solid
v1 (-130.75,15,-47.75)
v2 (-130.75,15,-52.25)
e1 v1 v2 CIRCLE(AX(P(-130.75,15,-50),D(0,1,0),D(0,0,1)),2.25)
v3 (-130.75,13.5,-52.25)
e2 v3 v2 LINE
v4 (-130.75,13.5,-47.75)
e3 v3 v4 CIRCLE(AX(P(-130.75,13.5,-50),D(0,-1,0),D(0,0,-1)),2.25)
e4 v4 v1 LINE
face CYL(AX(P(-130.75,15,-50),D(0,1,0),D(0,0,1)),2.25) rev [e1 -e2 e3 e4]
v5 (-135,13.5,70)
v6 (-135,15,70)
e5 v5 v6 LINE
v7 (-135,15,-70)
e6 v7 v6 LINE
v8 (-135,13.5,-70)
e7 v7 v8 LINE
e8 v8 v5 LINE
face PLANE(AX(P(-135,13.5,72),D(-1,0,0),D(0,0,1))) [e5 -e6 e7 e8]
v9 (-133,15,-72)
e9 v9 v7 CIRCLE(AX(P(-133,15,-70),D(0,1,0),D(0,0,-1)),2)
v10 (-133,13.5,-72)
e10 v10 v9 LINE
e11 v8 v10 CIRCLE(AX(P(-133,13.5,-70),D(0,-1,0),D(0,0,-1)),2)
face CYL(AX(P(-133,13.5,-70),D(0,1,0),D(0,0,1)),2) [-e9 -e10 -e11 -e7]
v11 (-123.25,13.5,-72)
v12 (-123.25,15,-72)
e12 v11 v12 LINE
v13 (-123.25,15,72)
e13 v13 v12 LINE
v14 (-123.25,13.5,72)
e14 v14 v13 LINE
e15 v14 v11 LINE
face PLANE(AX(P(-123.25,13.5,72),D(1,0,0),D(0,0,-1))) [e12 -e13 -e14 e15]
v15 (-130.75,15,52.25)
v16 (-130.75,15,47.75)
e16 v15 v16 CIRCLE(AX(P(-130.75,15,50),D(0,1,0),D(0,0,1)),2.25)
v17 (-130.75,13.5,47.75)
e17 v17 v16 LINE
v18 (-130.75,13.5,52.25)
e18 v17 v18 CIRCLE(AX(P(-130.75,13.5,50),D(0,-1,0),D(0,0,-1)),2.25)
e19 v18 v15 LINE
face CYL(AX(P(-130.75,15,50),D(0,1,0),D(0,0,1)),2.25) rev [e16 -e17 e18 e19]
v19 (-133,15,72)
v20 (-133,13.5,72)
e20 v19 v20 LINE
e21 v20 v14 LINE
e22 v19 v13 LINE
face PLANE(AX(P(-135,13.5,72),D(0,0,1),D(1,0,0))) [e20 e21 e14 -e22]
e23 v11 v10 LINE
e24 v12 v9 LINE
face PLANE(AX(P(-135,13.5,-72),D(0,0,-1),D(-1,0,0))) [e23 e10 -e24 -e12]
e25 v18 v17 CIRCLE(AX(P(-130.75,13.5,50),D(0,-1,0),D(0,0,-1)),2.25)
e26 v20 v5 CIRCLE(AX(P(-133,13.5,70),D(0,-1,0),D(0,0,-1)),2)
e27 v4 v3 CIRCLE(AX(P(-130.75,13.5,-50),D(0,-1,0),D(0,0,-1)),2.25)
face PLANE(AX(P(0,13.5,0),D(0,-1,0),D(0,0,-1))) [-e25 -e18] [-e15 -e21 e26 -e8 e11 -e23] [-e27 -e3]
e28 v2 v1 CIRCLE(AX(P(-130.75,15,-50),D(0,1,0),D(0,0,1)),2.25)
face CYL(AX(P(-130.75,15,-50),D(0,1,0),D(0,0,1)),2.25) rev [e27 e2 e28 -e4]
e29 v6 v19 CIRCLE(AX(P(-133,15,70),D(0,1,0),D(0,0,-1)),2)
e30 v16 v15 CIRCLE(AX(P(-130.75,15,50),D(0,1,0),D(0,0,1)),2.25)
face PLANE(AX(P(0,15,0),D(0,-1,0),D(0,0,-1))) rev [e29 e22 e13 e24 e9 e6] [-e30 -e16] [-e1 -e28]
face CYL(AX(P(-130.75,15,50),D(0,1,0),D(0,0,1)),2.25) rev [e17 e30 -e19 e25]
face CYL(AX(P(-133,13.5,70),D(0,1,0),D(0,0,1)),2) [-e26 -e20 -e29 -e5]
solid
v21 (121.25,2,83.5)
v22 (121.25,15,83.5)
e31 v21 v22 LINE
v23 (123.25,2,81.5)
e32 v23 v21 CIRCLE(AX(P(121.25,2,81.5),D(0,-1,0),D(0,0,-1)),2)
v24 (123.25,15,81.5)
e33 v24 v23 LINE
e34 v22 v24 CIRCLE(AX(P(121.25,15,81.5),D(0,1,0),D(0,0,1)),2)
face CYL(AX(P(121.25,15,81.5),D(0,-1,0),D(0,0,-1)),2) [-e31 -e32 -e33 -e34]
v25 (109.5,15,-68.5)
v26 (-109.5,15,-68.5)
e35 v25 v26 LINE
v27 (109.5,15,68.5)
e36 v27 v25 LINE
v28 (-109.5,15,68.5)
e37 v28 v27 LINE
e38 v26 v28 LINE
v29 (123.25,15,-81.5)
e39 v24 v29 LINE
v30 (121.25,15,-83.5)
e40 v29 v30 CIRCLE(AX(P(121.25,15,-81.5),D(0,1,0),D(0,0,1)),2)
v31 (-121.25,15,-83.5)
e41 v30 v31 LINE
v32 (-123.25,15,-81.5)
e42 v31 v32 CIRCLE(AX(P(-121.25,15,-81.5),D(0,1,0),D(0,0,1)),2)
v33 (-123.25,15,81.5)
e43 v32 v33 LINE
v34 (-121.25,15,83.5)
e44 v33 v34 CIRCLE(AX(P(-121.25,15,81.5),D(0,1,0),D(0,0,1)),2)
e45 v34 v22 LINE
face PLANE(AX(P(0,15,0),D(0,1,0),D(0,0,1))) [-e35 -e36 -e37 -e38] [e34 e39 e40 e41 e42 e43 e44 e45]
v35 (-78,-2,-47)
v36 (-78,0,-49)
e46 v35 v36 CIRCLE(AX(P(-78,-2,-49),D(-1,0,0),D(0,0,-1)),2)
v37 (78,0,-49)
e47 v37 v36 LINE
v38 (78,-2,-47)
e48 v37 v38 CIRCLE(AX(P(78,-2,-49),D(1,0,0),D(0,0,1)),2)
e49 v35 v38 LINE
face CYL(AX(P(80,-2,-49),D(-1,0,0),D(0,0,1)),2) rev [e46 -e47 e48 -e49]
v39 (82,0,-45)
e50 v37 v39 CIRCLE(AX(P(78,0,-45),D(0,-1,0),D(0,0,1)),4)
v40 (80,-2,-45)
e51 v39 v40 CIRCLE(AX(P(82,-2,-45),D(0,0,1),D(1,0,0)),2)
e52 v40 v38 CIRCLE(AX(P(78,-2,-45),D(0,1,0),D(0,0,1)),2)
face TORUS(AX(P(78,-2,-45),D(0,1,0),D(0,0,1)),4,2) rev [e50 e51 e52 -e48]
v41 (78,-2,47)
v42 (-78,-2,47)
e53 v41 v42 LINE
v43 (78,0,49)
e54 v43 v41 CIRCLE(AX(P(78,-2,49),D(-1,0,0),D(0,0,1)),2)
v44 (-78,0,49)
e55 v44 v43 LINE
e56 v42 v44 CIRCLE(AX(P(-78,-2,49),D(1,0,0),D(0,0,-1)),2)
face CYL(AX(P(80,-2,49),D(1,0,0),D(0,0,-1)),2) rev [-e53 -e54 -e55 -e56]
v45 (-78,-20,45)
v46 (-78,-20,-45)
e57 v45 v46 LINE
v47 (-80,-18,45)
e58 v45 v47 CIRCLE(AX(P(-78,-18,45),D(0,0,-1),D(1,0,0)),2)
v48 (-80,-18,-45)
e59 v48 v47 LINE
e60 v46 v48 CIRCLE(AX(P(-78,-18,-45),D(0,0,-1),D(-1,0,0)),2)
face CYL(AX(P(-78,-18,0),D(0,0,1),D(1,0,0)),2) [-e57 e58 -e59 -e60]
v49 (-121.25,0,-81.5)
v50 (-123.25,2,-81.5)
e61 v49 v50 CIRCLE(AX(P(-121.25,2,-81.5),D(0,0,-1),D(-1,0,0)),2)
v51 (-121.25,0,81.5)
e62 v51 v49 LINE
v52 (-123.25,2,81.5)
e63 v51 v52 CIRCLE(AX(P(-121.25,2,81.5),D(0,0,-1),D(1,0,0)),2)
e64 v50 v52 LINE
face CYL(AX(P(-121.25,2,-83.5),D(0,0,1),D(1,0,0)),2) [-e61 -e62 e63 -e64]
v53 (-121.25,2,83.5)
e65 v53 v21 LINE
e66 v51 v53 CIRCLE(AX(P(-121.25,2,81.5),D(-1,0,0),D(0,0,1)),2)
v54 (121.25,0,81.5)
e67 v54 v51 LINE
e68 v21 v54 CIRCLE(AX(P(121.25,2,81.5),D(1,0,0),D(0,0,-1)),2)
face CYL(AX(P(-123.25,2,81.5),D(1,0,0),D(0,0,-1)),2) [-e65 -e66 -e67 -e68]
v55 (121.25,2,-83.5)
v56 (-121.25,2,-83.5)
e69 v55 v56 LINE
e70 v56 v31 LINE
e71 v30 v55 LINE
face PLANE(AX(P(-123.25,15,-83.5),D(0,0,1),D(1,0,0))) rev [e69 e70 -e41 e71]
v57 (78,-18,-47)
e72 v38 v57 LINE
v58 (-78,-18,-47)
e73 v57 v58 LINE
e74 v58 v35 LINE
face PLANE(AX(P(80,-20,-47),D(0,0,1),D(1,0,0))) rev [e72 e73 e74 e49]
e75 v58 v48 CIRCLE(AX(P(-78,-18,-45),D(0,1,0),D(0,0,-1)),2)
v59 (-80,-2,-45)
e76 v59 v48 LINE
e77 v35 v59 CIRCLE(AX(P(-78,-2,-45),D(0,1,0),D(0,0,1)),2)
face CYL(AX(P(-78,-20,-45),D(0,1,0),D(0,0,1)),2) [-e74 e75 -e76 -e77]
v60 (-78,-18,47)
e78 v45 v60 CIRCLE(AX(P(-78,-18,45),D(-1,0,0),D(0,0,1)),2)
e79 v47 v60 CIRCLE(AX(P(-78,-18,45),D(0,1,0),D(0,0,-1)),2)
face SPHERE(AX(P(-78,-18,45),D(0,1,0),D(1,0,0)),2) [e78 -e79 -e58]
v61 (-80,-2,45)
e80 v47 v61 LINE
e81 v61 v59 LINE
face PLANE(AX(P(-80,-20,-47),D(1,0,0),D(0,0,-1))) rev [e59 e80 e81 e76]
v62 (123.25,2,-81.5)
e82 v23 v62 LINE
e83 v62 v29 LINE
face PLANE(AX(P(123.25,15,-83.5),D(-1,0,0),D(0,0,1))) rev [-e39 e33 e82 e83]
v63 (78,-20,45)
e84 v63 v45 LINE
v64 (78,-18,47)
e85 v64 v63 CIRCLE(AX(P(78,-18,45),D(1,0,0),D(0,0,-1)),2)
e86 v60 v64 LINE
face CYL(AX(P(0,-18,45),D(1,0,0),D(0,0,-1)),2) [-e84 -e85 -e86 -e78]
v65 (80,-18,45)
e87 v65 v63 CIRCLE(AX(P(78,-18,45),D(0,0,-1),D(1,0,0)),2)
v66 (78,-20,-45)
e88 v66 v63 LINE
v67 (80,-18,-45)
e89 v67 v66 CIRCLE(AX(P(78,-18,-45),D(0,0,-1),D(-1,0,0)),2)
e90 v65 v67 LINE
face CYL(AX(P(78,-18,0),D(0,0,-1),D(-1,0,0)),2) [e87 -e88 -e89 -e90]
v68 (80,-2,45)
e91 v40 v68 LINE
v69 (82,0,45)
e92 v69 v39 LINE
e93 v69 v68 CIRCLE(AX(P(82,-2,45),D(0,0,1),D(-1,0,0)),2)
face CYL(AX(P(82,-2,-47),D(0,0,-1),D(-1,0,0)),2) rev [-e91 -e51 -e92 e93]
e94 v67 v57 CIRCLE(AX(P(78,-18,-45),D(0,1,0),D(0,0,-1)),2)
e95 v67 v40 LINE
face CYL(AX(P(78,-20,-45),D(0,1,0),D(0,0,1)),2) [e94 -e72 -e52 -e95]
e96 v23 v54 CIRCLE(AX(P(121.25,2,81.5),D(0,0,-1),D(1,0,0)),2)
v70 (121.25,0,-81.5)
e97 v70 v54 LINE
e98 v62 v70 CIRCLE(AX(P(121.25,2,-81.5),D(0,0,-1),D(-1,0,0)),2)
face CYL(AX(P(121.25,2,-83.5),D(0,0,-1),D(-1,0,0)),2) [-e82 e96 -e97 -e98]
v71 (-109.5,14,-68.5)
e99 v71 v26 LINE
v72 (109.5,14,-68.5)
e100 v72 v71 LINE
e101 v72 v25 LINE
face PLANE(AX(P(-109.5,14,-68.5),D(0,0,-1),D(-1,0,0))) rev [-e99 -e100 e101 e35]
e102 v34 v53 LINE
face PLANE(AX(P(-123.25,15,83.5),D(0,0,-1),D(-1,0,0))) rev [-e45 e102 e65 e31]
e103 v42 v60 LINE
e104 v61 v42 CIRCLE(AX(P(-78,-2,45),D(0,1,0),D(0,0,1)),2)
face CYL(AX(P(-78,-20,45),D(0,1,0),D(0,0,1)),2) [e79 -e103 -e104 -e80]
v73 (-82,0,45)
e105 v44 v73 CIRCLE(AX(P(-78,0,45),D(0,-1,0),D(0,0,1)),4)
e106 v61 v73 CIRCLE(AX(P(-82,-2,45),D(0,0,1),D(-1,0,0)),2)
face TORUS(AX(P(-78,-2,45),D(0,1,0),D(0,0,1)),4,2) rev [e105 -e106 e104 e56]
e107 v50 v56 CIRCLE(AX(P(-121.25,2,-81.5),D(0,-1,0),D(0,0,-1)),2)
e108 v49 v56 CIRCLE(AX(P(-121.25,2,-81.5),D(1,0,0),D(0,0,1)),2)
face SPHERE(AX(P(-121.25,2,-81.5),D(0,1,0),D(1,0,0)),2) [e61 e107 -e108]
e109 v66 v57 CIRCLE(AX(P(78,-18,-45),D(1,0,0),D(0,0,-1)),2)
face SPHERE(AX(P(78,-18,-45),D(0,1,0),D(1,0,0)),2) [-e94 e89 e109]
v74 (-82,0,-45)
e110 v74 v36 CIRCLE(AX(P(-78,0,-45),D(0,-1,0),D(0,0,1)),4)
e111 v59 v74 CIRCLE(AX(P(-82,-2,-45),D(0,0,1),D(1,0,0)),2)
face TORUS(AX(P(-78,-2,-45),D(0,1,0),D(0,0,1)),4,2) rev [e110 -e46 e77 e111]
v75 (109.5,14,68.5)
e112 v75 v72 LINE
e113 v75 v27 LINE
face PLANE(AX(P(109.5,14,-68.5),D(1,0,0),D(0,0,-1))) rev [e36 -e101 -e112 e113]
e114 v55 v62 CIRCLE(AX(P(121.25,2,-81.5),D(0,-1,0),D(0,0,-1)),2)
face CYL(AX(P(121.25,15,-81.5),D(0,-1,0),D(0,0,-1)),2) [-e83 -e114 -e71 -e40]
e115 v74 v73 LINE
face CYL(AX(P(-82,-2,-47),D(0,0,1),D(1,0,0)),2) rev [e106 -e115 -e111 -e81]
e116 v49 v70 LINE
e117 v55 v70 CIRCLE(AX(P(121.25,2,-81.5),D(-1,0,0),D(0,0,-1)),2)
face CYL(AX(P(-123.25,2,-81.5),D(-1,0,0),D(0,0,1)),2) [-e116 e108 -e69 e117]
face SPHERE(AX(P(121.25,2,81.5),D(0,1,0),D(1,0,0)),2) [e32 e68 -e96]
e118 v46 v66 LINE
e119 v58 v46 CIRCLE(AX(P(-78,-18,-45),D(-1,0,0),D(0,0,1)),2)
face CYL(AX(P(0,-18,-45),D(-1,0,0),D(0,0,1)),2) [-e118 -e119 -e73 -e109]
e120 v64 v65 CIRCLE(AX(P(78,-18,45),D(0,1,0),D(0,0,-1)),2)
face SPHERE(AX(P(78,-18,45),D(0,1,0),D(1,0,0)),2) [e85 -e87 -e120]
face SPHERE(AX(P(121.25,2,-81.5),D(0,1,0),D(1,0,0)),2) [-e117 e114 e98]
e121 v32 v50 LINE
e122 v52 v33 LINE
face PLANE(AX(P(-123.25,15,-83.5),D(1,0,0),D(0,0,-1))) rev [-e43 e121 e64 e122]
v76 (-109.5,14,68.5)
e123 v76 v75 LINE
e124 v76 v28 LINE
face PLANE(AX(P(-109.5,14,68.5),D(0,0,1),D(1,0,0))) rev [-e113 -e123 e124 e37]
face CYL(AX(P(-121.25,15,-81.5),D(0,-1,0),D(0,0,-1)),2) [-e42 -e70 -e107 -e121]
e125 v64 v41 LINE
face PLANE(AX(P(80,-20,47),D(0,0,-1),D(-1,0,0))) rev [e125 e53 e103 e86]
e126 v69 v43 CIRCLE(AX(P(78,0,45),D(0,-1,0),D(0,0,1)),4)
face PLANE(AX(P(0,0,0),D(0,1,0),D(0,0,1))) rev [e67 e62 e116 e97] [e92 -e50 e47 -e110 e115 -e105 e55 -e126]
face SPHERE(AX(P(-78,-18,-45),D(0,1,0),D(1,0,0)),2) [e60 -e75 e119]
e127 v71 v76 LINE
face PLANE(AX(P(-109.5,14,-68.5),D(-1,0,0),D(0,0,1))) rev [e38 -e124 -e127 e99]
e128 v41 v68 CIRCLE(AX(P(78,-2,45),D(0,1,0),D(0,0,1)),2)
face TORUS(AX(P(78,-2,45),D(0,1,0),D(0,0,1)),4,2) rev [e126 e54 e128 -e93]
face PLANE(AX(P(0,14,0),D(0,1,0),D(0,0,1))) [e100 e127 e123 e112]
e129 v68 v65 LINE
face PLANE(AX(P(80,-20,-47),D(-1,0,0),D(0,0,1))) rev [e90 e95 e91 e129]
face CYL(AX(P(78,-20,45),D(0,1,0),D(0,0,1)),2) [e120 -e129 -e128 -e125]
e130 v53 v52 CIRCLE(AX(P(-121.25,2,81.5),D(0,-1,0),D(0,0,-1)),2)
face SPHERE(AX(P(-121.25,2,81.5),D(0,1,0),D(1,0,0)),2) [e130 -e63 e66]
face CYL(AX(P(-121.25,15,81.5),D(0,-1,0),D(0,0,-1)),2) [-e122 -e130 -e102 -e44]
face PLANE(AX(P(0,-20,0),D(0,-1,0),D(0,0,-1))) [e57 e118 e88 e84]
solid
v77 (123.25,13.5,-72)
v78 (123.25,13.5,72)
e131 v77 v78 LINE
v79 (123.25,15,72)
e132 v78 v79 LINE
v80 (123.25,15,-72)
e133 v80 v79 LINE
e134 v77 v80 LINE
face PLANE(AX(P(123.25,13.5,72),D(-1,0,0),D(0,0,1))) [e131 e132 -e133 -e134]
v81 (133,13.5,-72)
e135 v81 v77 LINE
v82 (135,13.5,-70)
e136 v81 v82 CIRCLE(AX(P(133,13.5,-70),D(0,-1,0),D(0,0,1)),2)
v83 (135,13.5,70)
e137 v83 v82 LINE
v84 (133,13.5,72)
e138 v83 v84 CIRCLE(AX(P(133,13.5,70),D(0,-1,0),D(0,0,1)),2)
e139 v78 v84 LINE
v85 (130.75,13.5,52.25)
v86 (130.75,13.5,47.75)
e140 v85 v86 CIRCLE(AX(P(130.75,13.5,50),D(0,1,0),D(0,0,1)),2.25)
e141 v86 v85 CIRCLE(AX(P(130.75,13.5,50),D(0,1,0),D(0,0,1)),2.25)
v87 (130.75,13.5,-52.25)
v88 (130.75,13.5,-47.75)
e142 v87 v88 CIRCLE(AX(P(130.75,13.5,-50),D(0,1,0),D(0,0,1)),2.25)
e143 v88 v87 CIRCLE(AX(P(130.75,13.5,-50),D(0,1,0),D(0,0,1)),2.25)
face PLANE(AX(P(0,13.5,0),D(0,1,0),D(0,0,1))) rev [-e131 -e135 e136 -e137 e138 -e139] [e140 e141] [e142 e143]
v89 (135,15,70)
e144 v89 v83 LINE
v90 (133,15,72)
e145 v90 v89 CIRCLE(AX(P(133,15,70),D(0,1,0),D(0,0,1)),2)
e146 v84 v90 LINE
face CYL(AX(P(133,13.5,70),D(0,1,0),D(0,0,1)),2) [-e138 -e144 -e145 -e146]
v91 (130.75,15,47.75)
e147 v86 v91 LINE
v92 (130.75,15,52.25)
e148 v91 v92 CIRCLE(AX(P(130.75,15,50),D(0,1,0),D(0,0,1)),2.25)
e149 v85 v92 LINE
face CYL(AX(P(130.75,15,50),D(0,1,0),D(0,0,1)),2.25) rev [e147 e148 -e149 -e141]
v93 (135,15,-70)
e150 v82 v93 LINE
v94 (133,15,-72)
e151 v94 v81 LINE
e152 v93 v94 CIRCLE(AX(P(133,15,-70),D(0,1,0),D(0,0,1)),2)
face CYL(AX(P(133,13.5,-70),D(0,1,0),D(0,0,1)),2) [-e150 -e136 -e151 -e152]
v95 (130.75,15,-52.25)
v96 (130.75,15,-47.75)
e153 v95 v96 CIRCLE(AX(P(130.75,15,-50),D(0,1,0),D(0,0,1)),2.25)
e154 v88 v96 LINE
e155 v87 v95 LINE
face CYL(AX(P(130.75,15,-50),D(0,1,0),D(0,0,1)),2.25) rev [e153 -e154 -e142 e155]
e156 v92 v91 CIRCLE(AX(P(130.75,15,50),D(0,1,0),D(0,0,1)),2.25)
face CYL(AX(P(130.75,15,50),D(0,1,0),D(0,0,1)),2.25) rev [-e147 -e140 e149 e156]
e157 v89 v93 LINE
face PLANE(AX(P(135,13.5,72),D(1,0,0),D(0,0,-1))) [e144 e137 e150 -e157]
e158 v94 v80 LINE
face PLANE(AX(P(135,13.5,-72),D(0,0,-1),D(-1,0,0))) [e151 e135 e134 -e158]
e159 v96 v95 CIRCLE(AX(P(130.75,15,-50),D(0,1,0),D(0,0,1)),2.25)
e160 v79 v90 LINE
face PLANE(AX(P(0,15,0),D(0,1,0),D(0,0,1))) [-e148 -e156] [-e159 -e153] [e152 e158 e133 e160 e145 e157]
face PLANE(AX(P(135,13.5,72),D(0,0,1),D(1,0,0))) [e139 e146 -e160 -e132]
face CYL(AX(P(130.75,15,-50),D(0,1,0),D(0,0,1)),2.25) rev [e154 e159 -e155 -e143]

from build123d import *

# Parameters (mm, degrees)
SKETCH_1_W                       = 246.5
SKETCH_1_H                       = 167
EXTRUDE_1_DEPTH                  = 15
SKETCH_3_W                       = 160
SKETCH_3_H                       = 94
EXTRUDE_2_DEPTH                  = 20
FILLET_1_R                       = 2
SKETCH_4_W                       = 219
SKETCH_4_H                       = 137
CUT_EXTRUDE_1_DEPTH              = 1
SKETCH_5_W                       = 11.75
SKETCH_5_H                       = 144
EXTRUDE_3_DEPTH                  = 1.5
EXTRUDE_3_2_DEPTH                = 1.5
SKETCH_6_W                       = 2.25
SKETCH_6_H                       = 35
HOLE_WIZARD_4_5_4_5_1_AT_2_COUNT = 2
HOLE_WIZARD_4_5_4_5_1_AT_2_PITCH = 100
HOLE_WIZARD_4_5_4_5_1_AT_3_COUNT = 2
HOLE_WIZARD_4_5_4_5_1_AT_3_PITCH = 279.968301777
HOLE_WIZARD_4_5_4_5_1_AT_4_COUNT = 2
HOLE_WIZARD_4_5_4_5_1_AT_4_PITCH = 261.5
FILLET_2_R                       = 2
FILLET_3_R                       = 2


with BuildPart() as part:
    # 草图1 → 凸台-拉伸1 (new body)
    with BuildSketch(Plane(origin=(0, 0, 0), x_dir=(1, 0, 0), z_dir=(0, 1, 0))):
        Rectangle(SKETCH_1_W, SKETCH_1_H)
    extrude(amount=EXTRUDE_1_DEPTH)

    # 草图3 → 凸台-拉伸2 (add)
    with BuildSketch(Plane.XZ):
        Rectangle(SKETCH_3_W, SKETCH_3_H)
    extrude(amount=EXTRUDE_2_DEPTH)

    # 圆角1
    fillet_1_edges = [part.edges().sort_by_distance(p)[0] for p in [
        (-80, 0, 0),
        (-80, -10, 47),
        (0, 0, -47),
        (-80, -10, -47),
        (80, 0, 0),
        (80, -10, -47),
        (0, 0, 47),
        (80, -10, 47),
        (-80, -20, 0),
        (0, -20, -47),
        (80, -20, 0),
        (0, -20, 47),
        (0, 0, 83.5),
        (-123.25, 0, 0),
        (0, 0, -83.5),
        (123.25, 0, 0),
        (123.25, 7.5, 83.5),
        (-123.25, 7.5, 83.5),
        (-123.25, 7.5, -83.5),
        (123.25, 7.5, -83.5),
    ]]
    fillet(fillet_1_edges, radius=FILLET_1_R)

    # 草图4 → 切除-拉伸1 (cut)
    with BuildSketch(Plane(origin=(0, 15, 0), x_dir=(1, 0, 0), z_dir=(0, 1, 0))):
        Rectangle(SKETCH_4_W, SKETCH_4_H)
    extrude(amount=-CUT_EXTRUDE_1_DEPTH, mode=Mode.SUBTRACT)


with BuildPart() as body_2:
    # 草图5 → 凸台-拉伸3 (new body)
    with BuildSketch(Plane(origin=(0, 15, 0), x_dir=(1, 0, 0), z_dir=(0, 1, 0))):
        with Locations((129.125, 0)):
            Rectangle(SKETCH_5_W, SKETCH_5_H)
    extrude(amount=-EXTRUDE_3_DEPTH)

    # 草图6 → Ø4.5 (4.5) 直径孔1 (revolve, cut)
    with BuildSketch(Plane(origin=(130.75, 15, -50), x_dir=(0, 0, 1), z_dir=(1, 0, 0))):
        with Locations((1.125, 17.5)):
            Rectangle(SKETCH_6_W, SKETCH_6_H)
    hole_wizard_4_5_4_5_1 = revolve(axis=Axis((130.75, 21.35, -50), (0, -1, 0)), mode=Mode.SUBTRACT)

    # Ø4.5 (4.5) 直径孔1 at 2: Ø4.5 (4.5) 直径孔1 ×2
    with Locations(*[(0, 0, i * HOLE_WIZARD_4_5_4_5_1_AT_2_PITCH) for i in range(1, HOLE_WIZARD_4_5_4_5_1_AT_2_COUNT)]):
        add(hole_wizard_4_5_4_5_1, mode=Mode.SUBTRACT)

    # 圆角2
    fillet_2_edges = [body_2.edges().sort_by_distance(p)[0] for p in [
        (135, 14.25, -72),
        (135, 14.25, 72),
    ]]
    fillet(fillet_2_edges, radius=FILLET_2_R)


with BuildPart() as body_3:
    # 草图5 → Extrude 3 2 (new body)
    with BuildSketch(Plane(origin=(0, 15, 0), x_dir=(1, 0, 0), z_dir=(0, 1, 0))):
        with Locations((-129.125, 0)):
            Rectangle(SKETCH_5_W, SKETCH_5_H)
    extrude(amount=-EXTRUDE_3_2_DEPTH)

    # Ø4.5 (4.5) 直径孔1 at 3: Ø4.5 (4.5) 直径孔1 ×2
    with Locations(*[Vector(-0.9340343115275901, 0, 0.35718329312718555) * (i * HOLE_WIZARD_4_5_4_5_1_AT_3_PITCH) for i in range(1, HOLE_WIZARD_4_5_4_5_1_AT_3_COUNT)]):
        add(hole_wizard_4_5_4_5_1, mode=Mode.SUBTRACT)

    # Ø4.5 (4.5) 直径孔1 at 4: Ø4.5 (4.5) 直径孔1 ×2
    with Locations(*[(-i * HOLE_WIZARD_4_5_4_5_1_AT_4_PITCH, 0, 0) for i in range(1, HOLE_WIZARD_4_5_4_5_1_AT_4_COUNT)]):
        add(hole_wizard_4_5_4_5_1, mode=Mode.SUBTRACT)

    # 圆角3
    fillet_3_edges = [body_3.edges().sort_by_distance(p)[0] for p in [
        (-135, 14.25, -72),
        (-135, 14.25, 72),
    ]]
    fillet(fillet_3_edges, radius=FILLET_3_R)


solid = Compound([part.part, body_2.part, body_3.part])
